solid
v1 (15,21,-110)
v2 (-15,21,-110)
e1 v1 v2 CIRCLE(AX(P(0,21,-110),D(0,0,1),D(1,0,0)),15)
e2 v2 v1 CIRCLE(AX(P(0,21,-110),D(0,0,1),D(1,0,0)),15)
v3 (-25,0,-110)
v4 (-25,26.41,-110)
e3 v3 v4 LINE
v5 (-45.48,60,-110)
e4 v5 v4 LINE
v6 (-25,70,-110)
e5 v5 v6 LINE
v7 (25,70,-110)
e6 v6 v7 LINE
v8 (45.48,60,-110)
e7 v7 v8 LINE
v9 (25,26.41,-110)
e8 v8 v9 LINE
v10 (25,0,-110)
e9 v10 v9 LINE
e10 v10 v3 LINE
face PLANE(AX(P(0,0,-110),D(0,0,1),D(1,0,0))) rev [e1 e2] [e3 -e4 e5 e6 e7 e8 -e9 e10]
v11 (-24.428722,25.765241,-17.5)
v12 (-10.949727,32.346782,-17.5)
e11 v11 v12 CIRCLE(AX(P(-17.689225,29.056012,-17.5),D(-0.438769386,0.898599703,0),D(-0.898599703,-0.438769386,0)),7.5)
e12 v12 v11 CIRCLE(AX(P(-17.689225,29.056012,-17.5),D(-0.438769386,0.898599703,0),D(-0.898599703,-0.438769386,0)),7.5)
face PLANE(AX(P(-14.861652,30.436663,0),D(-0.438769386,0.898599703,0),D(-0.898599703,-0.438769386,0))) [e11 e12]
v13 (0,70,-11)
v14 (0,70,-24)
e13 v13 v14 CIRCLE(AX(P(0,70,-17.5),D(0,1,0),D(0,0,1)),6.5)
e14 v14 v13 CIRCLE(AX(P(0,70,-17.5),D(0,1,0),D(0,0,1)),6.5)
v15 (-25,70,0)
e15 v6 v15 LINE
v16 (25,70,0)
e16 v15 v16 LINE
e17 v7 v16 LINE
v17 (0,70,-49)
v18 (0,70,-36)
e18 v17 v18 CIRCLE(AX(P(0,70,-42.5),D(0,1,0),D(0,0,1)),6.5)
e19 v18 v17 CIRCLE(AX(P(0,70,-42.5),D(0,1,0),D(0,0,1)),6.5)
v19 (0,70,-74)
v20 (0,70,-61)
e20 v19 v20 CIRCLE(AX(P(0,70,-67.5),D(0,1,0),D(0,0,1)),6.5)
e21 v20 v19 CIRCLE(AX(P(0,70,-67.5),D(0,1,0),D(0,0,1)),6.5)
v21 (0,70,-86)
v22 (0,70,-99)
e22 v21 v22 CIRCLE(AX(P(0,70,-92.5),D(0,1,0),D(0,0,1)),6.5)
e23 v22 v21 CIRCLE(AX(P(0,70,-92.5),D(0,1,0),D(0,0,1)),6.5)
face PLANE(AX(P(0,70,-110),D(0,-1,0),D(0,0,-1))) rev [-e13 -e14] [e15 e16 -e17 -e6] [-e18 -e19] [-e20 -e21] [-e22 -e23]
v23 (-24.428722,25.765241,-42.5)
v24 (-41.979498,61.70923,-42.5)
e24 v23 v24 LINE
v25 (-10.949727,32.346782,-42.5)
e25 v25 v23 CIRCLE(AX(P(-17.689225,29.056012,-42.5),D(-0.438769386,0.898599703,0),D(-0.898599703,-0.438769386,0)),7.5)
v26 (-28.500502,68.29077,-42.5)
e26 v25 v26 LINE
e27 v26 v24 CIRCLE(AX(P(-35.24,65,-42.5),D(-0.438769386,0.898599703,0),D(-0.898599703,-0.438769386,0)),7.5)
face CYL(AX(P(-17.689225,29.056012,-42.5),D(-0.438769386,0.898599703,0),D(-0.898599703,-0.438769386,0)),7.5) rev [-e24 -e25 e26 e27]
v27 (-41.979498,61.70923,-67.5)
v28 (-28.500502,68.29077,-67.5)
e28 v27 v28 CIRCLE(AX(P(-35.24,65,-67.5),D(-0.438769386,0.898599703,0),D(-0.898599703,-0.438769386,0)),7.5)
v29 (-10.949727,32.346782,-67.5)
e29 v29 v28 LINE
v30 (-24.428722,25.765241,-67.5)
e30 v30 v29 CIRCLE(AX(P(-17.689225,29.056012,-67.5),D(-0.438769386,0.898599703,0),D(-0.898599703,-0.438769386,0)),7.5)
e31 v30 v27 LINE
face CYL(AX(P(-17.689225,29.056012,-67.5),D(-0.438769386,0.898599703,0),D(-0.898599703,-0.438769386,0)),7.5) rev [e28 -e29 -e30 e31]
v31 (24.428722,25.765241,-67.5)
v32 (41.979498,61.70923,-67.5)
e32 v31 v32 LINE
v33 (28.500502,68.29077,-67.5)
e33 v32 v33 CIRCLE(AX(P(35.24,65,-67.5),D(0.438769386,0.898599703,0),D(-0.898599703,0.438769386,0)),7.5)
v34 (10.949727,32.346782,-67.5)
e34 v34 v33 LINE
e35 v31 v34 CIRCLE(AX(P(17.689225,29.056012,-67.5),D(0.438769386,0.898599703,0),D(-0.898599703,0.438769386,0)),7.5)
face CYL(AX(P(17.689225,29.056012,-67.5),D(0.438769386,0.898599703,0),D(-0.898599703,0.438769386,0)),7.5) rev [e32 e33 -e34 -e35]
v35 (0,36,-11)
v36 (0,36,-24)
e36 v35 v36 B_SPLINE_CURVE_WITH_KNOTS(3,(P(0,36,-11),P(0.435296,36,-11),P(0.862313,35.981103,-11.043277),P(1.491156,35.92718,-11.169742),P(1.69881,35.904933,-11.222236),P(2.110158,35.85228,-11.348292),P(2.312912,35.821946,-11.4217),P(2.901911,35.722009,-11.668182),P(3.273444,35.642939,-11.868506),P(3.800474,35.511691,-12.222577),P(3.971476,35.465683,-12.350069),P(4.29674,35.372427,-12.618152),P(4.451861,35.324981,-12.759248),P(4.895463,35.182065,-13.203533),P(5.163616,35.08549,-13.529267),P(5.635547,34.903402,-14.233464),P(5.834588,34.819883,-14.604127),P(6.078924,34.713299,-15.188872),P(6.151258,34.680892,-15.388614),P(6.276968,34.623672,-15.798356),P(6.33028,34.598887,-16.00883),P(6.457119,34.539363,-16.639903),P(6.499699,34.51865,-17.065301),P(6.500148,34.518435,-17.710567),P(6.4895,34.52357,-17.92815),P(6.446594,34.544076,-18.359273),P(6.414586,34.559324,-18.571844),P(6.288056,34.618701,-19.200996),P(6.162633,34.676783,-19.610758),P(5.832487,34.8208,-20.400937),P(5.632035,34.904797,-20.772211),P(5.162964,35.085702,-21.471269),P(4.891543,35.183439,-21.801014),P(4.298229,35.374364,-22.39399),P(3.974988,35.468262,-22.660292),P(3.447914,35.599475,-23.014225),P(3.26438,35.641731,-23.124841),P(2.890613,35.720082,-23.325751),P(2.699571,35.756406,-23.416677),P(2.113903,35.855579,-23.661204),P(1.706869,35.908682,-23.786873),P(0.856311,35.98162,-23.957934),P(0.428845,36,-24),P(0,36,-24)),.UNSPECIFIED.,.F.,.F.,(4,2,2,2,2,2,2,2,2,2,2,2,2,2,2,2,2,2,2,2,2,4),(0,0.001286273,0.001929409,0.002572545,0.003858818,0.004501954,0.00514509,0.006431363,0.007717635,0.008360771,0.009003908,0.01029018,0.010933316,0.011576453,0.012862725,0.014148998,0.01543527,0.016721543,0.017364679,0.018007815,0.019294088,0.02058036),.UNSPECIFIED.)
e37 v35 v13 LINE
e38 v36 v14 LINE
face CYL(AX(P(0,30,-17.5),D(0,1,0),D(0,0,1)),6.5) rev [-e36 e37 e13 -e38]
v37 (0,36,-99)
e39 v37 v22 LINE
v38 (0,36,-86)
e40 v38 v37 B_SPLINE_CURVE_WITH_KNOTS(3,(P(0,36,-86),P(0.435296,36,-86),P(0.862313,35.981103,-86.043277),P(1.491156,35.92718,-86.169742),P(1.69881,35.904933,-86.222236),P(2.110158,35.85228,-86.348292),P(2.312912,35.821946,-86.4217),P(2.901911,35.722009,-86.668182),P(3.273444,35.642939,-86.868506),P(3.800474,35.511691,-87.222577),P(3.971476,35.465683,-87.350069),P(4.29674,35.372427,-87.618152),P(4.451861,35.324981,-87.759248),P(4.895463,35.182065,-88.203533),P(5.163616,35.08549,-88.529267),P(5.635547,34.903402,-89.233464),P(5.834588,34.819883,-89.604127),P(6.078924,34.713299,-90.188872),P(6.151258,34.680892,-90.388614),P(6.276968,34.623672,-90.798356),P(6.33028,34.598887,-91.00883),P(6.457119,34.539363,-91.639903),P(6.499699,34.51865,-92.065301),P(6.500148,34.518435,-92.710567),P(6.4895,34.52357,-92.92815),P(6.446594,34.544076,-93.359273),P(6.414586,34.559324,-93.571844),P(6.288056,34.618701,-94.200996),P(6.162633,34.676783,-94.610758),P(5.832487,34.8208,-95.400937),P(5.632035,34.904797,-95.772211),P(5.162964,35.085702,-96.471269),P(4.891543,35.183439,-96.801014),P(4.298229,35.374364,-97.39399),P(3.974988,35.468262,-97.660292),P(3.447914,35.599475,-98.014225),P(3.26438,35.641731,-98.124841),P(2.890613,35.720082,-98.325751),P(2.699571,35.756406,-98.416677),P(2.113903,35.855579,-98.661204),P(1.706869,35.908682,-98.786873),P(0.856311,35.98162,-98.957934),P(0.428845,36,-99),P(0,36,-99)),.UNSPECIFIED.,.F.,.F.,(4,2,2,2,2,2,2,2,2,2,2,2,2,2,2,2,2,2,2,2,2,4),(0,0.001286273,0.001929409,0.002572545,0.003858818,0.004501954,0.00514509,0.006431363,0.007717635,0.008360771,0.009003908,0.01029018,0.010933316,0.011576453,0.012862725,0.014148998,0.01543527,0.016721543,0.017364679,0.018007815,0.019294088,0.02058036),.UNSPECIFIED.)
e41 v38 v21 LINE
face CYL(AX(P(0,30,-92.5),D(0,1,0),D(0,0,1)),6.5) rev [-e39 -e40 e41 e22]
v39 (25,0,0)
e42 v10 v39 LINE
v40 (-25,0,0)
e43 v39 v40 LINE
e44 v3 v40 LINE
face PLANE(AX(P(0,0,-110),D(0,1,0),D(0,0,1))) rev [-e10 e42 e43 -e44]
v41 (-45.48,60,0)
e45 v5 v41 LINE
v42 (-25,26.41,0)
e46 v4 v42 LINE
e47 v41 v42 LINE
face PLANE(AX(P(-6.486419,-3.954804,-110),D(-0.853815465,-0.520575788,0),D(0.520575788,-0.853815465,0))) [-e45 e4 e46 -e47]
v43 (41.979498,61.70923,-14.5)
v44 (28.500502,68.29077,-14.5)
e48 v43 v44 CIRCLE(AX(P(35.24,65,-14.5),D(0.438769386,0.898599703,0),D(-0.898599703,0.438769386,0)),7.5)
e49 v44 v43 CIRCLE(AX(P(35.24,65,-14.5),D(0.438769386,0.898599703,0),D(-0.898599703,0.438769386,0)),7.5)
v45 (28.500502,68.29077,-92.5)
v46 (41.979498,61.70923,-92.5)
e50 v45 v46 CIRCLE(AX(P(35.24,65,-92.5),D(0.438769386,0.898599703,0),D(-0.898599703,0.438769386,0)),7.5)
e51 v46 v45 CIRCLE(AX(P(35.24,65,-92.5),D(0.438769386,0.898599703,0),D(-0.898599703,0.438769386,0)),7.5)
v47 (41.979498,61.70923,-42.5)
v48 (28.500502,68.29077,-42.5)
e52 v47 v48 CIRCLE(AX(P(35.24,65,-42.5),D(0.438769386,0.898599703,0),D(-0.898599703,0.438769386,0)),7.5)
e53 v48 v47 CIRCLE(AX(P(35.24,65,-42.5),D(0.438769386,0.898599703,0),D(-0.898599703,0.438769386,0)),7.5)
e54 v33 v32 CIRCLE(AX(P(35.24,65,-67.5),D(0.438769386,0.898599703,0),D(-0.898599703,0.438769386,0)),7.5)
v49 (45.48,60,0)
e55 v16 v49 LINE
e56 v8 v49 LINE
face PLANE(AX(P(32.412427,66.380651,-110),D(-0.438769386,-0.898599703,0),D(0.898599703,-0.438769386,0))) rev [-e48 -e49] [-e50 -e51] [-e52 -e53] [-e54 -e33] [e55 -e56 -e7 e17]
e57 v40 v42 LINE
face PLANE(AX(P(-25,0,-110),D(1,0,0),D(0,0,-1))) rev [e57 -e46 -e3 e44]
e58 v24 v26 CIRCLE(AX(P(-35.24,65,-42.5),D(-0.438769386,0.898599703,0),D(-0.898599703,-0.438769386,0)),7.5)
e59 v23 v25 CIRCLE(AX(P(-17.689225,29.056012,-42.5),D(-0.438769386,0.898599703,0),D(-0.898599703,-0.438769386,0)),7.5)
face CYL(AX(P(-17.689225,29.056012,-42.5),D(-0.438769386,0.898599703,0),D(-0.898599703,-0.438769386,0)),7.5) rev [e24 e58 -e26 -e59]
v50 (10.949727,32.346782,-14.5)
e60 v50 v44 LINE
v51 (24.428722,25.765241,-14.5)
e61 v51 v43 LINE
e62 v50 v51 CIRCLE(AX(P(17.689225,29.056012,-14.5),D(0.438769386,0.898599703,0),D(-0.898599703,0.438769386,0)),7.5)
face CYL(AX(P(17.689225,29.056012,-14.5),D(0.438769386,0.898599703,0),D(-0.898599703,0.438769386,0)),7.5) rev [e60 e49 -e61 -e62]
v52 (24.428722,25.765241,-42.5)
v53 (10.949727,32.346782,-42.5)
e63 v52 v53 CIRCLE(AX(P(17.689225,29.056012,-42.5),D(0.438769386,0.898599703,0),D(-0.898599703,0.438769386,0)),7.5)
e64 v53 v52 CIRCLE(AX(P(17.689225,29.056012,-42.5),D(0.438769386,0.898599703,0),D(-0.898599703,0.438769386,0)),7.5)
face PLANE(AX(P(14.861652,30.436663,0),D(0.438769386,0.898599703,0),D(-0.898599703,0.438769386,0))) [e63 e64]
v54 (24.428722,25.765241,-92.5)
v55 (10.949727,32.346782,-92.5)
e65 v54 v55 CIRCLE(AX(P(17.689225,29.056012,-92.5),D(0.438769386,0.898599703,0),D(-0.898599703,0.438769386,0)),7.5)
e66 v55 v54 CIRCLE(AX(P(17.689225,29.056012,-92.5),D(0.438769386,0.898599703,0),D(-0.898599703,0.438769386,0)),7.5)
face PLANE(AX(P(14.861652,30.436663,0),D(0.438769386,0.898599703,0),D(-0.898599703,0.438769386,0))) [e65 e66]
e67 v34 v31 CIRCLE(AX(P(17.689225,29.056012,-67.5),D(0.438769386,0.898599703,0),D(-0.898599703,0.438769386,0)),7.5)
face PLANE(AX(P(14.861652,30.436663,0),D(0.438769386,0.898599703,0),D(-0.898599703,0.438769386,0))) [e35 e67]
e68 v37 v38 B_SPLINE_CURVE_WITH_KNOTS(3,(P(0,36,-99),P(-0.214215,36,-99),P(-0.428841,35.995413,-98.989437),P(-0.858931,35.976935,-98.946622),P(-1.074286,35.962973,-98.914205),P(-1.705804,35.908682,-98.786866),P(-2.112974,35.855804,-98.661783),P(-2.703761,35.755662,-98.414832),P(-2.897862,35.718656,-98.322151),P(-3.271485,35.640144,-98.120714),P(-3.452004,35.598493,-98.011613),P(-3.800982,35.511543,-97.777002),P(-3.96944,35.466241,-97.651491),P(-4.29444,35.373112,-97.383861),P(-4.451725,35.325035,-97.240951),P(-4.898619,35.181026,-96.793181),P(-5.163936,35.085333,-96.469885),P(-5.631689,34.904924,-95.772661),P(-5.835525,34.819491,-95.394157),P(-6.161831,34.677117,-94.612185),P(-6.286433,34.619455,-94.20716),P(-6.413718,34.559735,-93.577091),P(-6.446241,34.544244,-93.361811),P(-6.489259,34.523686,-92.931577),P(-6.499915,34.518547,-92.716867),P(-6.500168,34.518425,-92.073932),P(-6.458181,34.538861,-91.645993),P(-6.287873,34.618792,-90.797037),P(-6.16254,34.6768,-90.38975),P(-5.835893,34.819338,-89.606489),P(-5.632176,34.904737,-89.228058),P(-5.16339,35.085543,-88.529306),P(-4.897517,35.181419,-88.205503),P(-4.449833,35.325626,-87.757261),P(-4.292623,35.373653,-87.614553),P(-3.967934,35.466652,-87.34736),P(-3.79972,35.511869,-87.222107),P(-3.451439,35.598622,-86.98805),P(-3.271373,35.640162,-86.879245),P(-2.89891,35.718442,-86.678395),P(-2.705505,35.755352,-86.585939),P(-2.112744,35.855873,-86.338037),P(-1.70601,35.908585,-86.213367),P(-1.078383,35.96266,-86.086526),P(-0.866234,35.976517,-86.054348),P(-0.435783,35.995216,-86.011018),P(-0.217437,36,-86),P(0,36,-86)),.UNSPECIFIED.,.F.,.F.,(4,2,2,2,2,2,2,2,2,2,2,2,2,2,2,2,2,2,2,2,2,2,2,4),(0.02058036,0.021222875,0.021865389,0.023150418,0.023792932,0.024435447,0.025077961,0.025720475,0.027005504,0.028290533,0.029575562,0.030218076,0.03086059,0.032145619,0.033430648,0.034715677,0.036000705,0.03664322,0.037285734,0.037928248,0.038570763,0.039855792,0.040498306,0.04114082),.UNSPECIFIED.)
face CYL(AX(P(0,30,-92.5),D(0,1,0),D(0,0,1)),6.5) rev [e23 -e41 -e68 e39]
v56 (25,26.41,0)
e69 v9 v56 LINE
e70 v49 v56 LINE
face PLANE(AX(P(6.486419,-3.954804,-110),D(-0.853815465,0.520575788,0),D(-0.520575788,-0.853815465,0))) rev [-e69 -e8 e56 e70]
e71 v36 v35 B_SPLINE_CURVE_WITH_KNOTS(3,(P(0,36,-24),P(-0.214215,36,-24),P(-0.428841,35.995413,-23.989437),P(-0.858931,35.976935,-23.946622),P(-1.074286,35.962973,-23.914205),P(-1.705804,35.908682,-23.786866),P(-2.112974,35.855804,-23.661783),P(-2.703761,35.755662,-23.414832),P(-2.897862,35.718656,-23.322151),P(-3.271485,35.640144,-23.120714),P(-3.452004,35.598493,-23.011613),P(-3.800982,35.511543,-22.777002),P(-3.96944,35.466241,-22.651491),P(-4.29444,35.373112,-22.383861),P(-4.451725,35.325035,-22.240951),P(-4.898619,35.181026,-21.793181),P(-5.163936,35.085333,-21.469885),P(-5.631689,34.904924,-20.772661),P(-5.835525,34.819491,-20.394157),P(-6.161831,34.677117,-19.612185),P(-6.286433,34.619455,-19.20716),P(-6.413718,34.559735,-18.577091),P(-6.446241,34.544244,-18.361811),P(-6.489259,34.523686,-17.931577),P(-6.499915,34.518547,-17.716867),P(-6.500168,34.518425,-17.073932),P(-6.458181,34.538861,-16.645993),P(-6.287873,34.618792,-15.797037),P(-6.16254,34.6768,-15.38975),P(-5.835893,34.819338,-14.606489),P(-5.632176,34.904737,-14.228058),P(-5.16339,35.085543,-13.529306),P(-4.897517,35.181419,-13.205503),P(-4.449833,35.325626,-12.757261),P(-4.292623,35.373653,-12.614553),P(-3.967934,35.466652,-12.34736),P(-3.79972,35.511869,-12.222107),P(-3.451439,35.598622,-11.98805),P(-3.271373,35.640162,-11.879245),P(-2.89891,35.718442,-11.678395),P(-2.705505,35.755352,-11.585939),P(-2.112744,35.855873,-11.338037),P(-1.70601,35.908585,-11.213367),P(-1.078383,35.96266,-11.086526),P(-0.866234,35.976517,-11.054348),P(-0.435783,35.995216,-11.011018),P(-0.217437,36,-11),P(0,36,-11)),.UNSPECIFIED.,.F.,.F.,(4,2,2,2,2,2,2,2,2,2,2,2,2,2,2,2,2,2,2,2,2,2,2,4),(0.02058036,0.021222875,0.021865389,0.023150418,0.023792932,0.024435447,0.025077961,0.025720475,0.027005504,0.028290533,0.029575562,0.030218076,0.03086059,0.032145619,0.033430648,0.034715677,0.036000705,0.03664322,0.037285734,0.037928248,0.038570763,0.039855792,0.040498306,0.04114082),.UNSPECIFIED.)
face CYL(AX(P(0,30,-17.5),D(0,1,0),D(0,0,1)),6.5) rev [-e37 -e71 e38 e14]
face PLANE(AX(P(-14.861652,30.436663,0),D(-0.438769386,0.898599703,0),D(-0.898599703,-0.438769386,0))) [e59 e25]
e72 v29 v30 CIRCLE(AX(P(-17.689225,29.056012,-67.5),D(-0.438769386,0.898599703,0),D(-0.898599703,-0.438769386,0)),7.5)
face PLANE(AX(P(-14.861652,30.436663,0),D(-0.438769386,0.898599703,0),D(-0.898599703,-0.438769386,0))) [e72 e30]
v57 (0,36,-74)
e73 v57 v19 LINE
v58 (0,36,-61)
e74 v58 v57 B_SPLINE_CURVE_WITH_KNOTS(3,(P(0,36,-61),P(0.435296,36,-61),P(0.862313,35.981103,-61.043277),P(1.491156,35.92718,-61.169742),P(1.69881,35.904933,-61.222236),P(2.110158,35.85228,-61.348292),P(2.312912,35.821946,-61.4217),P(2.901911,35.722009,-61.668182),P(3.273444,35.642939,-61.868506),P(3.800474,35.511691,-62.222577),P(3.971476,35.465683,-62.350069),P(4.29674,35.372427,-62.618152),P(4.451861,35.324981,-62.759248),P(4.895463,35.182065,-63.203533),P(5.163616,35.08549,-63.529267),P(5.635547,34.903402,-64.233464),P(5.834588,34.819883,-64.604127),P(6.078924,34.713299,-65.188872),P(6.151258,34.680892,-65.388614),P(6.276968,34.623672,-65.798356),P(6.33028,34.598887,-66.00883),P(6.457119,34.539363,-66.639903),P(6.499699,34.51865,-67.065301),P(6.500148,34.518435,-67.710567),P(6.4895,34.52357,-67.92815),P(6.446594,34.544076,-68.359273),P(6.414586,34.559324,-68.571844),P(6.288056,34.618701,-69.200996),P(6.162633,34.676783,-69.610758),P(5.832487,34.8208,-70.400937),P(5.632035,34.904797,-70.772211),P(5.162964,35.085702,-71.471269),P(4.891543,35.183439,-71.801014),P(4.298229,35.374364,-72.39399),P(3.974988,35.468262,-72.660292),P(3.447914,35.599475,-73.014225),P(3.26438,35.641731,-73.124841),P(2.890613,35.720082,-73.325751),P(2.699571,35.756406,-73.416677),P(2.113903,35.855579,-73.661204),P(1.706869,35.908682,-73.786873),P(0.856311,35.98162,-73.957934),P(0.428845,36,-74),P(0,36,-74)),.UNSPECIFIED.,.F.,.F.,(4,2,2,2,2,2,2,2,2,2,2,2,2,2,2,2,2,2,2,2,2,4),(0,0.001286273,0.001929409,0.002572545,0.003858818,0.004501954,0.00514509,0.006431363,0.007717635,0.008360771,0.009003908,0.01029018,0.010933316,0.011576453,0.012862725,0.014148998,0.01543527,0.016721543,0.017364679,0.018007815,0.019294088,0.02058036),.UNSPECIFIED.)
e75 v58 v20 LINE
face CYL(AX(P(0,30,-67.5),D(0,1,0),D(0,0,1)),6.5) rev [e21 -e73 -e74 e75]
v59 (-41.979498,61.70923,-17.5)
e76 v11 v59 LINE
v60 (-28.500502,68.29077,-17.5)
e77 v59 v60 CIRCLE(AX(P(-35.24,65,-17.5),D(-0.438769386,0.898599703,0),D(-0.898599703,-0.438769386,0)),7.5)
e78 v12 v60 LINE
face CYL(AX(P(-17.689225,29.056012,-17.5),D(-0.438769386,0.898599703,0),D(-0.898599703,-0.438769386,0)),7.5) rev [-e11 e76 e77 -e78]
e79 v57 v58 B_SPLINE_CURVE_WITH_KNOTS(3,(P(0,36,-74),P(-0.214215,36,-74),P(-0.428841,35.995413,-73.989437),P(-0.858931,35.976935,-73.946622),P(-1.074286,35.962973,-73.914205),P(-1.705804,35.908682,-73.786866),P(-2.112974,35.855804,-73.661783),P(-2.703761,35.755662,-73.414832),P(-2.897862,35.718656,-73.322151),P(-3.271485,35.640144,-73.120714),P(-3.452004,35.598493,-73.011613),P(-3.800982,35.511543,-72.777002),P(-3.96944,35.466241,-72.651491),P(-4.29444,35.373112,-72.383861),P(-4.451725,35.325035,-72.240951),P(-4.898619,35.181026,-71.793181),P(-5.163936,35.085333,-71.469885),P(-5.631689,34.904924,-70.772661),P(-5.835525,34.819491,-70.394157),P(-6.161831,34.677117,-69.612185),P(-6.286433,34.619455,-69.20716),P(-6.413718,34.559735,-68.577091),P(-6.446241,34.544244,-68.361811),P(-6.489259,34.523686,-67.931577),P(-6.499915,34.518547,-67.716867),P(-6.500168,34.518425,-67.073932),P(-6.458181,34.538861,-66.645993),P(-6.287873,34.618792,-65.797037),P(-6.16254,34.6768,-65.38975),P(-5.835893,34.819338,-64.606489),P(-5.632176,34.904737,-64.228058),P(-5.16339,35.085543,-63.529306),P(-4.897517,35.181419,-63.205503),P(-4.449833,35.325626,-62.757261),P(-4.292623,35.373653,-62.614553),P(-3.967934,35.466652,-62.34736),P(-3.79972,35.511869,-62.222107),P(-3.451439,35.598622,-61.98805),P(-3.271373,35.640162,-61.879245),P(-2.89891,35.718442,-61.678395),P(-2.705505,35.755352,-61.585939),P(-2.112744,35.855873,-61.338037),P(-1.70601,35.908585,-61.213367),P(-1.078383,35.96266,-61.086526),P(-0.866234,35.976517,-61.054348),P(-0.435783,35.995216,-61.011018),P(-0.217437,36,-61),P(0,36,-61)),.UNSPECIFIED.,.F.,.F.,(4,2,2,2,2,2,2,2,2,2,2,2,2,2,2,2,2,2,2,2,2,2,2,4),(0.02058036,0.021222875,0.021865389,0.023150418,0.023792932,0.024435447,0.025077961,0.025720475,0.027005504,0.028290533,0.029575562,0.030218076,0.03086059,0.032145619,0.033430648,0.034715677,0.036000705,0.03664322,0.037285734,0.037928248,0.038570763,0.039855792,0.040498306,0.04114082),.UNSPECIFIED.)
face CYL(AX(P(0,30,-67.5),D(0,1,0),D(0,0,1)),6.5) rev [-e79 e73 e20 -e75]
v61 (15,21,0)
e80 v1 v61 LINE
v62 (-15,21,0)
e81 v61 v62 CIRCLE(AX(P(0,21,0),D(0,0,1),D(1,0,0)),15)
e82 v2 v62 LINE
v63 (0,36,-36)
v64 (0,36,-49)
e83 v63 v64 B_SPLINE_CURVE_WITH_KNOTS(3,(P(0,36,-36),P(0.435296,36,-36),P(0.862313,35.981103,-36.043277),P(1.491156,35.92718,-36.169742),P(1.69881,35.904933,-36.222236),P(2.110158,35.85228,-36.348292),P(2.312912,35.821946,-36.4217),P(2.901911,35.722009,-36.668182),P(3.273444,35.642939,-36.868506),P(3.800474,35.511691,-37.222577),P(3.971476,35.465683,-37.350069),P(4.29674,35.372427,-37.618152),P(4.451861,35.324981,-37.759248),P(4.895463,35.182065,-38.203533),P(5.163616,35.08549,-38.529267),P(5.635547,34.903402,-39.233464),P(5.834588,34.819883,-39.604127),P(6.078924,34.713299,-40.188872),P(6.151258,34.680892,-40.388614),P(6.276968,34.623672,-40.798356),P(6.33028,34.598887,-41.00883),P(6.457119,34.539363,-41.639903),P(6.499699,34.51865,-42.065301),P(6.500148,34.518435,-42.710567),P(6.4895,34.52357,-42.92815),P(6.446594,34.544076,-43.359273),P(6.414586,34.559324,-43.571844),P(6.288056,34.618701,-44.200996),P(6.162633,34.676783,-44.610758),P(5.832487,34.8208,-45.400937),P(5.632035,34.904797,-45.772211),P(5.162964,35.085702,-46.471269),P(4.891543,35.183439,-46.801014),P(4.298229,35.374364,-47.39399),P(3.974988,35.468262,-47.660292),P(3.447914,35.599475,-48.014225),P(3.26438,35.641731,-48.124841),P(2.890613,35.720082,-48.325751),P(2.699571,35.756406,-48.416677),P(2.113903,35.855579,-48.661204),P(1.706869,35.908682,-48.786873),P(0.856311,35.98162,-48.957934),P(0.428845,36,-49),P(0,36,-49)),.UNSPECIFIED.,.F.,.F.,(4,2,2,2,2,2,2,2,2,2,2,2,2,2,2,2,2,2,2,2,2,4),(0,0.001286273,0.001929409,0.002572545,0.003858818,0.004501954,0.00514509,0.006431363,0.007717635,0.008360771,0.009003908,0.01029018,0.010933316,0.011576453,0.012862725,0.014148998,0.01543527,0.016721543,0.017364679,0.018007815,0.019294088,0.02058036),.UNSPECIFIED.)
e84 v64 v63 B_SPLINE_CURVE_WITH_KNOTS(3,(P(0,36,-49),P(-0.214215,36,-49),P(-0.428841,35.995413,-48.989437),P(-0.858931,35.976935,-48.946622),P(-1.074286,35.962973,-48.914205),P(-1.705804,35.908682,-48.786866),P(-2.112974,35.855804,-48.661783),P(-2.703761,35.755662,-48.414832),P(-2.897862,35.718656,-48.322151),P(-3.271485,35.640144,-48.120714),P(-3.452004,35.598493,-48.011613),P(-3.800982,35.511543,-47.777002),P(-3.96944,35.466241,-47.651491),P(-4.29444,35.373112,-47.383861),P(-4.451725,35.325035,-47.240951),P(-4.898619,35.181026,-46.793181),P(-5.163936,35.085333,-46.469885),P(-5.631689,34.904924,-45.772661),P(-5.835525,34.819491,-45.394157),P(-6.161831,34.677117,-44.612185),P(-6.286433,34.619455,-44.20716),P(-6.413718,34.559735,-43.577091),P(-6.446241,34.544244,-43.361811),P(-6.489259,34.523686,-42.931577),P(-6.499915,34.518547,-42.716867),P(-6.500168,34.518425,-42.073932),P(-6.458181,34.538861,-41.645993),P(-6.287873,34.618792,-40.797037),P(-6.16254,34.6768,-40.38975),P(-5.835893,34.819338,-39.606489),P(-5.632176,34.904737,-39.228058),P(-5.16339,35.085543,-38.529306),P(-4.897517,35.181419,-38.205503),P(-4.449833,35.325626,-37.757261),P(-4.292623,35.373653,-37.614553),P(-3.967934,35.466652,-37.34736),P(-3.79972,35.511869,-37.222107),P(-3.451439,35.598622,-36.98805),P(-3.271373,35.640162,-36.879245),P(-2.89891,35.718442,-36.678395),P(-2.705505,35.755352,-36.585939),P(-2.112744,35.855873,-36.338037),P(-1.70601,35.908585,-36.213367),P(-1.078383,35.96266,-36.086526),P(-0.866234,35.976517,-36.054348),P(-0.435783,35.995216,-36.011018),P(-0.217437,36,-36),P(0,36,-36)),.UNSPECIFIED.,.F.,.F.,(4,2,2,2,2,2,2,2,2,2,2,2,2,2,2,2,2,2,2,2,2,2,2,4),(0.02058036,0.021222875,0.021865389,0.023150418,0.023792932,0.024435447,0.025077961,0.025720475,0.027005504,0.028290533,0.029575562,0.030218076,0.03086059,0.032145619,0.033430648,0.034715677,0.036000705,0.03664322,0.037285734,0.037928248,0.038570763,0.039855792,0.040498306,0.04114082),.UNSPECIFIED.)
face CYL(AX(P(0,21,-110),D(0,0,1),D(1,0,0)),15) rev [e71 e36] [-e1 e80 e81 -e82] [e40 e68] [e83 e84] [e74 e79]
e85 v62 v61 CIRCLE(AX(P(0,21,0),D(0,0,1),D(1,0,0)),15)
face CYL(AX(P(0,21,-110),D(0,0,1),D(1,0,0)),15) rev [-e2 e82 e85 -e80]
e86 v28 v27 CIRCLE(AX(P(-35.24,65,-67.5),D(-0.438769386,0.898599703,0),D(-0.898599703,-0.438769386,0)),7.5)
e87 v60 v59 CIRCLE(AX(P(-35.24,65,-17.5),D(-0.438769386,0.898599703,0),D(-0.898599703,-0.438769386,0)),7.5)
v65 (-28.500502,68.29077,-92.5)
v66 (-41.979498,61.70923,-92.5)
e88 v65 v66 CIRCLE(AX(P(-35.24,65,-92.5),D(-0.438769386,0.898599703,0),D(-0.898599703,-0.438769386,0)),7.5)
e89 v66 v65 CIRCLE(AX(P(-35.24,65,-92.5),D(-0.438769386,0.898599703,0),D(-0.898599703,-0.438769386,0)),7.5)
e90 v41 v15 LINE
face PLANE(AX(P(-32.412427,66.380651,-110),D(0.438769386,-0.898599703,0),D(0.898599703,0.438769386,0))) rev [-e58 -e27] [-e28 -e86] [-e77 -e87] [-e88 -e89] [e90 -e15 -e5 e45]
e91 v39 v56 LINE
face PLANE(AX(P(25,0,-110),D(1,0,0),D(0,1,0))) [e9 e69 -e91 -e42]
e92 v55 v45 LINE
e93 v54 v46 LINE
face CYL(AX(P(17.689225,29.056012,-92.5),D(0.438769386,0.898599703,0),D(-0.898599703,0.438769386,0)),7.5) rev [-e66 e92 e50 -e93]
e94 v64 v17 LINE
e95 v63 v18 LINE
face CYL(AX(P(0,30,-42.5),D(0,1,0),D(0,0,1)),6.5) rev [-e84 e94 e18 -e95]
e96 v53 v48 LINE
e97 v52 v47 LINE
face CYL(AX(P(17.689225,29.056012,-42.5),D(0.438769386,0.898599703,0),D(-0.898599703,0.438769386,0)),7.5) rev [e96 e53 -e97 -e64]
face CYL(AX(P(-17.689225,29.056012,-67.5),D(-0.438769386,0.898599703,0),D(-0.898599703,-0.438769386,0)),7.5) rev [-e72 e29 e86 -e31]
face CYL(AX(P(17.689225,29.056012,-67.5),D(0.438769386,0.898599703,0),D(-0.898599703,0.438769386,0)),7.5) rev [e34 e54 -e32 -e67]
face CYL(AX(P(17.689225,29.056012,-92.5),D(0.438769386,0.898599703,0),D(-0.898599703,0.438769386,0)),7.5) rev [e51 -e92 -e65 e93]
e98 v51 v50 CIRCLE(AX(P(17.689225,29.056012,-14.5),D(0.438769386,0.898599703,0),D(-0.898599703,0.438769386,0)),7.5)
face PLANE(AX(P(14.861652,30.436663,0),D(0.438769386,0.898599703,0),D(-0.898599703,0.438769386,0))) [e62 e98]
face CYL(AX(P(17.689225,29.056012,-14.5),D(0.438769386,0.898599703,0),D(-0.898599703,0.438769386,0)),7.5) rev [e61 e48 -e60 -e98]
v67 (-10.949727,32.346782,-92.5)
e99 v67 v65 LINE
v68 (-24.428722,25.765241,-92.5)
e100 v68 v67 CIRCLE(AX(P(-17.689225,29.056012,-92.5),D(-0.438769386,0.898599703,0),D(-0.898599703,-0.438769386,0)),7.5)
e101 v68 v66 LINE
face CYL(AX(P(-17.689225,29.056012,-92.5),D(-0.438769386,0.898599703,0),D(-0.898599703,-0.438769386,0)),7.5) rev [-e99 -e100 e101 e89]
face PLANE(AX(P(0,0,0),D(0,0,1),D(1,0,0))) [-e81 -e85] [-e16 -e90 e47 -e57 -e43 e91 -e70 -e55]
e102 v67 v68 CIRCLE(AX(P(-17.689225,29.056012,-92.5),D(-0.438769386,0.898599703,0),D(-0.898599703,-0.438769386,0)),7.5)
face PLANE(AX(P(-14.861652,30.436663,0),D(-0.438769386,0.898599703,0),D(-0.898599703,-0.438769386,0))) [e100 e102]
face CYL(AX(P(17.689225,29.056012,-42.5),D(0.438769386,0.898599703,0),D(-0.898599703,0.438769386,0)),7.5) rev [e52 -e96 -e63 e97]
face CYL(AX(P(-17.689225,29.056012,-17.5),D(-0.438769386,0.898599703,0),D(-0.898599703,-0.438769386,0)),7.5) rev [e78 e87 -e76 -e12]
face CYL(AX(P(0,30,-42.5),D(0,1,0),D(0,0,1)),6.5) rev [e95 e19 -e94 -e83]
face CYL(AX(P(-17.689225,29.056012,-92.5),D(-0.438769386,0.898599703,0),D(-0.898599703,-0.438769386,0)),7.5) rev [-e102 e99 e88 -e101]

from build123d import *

# Parameters (mm, degrees)
BLOCK_PROFILE_SKETCH_R      = 15
ENGINE_BLOCK_DEPTH          = 110
BANK_1_CYLINDER_BORES_DEPTH = 40
BANK_2_BORES_SKETCH_R       = 7.5
BANK_2_CYLINDER_BORES_DEPTH = 40
TOP_DECK_BORES_SKETCH_R     = 6.5
TOP_DECK_BORES_DEPTH        = 40


with BuildPart() as part:
    # Block Profile Sketch → Engine Block (new body)
    with BuildSketch(Plane.XY):
        Polygon((-25, 0), (0, 0), (25, 0), (25, 26.41), (45.48, 60), (25, 70), (0, 70), (-25, 70), (-45.48, 60), (-25, 26.41), align=None)
        with Locations((0, 21)):
            Circle(BLOCK_PROFILE_SKETCH_R, mode=Mode.SUBTRACT)
    extrude(amount=-ENGINE_BLOCK_DEPTH)

    # Bank 1 Bores Sketch → Bank 1 Cylinder Bores (cut)
    with BuildSketch(Plane(origin=(32.412427151, 66.380650805, 0), x_dir=(0.8985997027642283, -0.43876938611534955, 0), z_dir=(0.4387693861153495, 0.8985997027642282, 0))):
        with BuildLine():
            ThreePointArc((3.146643428, 100), (-4.353356572, 92.5), (3.146643428, 85))
            Line((3.146643428, 85), (3.146643428, 92.5))
            Line((3.146643428, 92.5), (3.146643428, 100))
        make_face()
        with BuildLine():
            Line((3.146643428, 92.5), (3.146643428, 85))
            ThreePointArc((3.146643428, 85), (8.449944287, 87.196699141), (10.646643428, 92.5))
            Line((10.646643428, 92.5), (3.146643428, 92.5))
        make_face()
        with BuildLine():
            Line((3.146643428, 100), (3.146643428, 92.5))
            Line((3.146643428, 92.5), (10.646643428, 92.5))
            ThreePointArc((10.646643428, 92.5), (8.449944287, 97.803300859), (3.146643428, 100))
        make_face()
        with BuildLine():
            Line((3.146643428, 92.5), (3.146643428, 85))
            ThreePointArc((3.146643428, 85), (8.449944287, 87.196699141), (10.646643428, 92.5))
            Line((10.646643428, 92.5), (3.146643428, 92.5))
        make_face()
        with BuildLine():
            Line((3.146643428, 100), (3.146643428, 92.5))
            Line((3.146643428, 92.5), (10.646643428, 92.5))
            ThreePointArc((10.646643428, 92.5), (8.449944287, 97.803300859), (3.146643428, 100))
        make_face()
        with BuildLine():
            Line((3.146643428, 67.5), (3.146643428, 60))
            ThreePointArc((3.146643428, 60), (8.449944287, 62.196699141), (10.646643428, 67.5))
            Line((10.646643428, 67.5), (3.146643428, 67.5))
        make_face()
        with BuildLine():
            Line((3.146643428, 75), (3.146643428, 67.5))
            Line((3.146643428, 67.5), (10.646643428, 67.5))
            ThreePointArc((10.646643428, 67.5), (8.449944287, 72.803300859), (3.146643428, 75))
        make_face()
        with BuildLine():
            Line((3.146643428, 67.5), (3.146643428, 60))
            ThreePointArc((3.146643428, 60), (8.449944287, 62.196699141), (10.646643428, 67.5))
            Line((10.646643428, 67.5), (3.146643428, 67.5))
        make_face()
        with BuildLine():
            Line((3.146643428, 75), (3.146643428, 67.5))
            Line((3.146643428, 67.5), (10.646643428, 67.5))
            ThreePointArc((10.646643428, 67.5), (8.449944287, 72.803300859), (3.146643428, 75))
        make_face()
        with BuildLine():
            ThreePointArc((3.146643428, 75), (-4.353356572, 67.5), (3.146643428, 60))
            Line((3.146643428, 60), (3.146643428, 67.5))
            Line((3.146643428, 67.5), (3.146643428, 75))
        make_face()
        with BuildLine():
            ThreePointArc((3.146643428, 50), (-4.353356572, 42.5), (3.146643428, 35))
            Line((3.146643428, 35), (3.146643428, 42.5))
            Line((3.146643428, 42.5), (3.146643428, 50))
        make_face()
        with BuildLine():
            Line((3.146643428, 42.5), (3.146643428, 35))
            ThreePointArc((3.146643428, 35), (8.449944287, 37.196699141), (10.646643428, 42.5))
            Line((10.646643428, 42.5), (3.146643428, 42.5))
        make_face()
        with BuildLine():
            Line((3.146643428, 50), (3.146643428, 42.5))
            Line((3.146643428, 42.5), (10.646643428, 42.5))
            ThreePointArc((10.646643428, 42.5), (8.449944287, 47.803300859), (3.146643428, 50))
        make_face()
        with BuildLine():
            Line((3.146643428, 42.5), (3.146643428, 35))
            ThreePointArc((3.146643428, 35), (8.449944287, 37.196699141), (10.646643428, 42.5))
            Line((10.646643428, 42.5), (3.146643428, 42.5))
        make_face()
        with BuildLine():
            Line((3.146643428, 50), (3.146643428, 42.5))
            Line((3.146643428, 42.5), (10.646643428, 42.5))
            ThreePointArc((10.646643428, 42.5), (8.449944287, 47.803300859), (3.146643428, 50))
        make_face()
        with BuildLine():
            ThreePointArc((3.146643428, 22), (-4.353356572, 14.5), (3.146643428, 7))
            Line((3.146643428, 7), (3.146643428, 14.5))
            Line((3.146643428, 14.5), (3.146643428, 22))
        make_face()
        with BuildLine():
            Line((3.146643428, 14.5), (3.146643428, 7))
            ThreePointArc((3.146643428, 7), (8.449944287, 9.196699141), (10.646643428, 14.5))
            Line((10.646643428, 14.5), (3.146643428, 14.5))
        make_face()
        with BuildLine():
            Line((3.146643428, 22), (3.146643428, 14.5))
            Line((3.146643428, 14.5), (10.646643428, 14.5))
            ThreePointArc((10.646643428, 14.5), (8.449944287, 19.803300859), (3.146643428, 22))
        make_face()
        with BuildLine():
            Line((3.146643428, 14.5), (3.146643428, 7))
            ThreePointArc((3.146643428, 7), (8.449944287, 9.196699141), (10.646643428, 14.5))
            Line((10.646643428, 14.5), (3.146643428, 14.5))
        make_face()
        with BuildLine():
            Line((3.146643428, 22), (3.146643428, 14.5))
            Line((3.146643428, 14.5), (10.646643428, 14.5))
            ThreePointArc((10.646643428, 14.5), (8.449944287, 19.803300859), (3.146643428, 22))
        make_face()
    extrude(amount=-BANK_1_CYLINDER_BORES_DEPTH, mode=Mode.SUBTRACT)

    # Bank 2 Bores Sketch → Bank 2 Cylinder Bores (cut)
    with BuildSketch(Plane(origin=(-32.412427151, 66.380650805, 0), x_dir=(0.8985997027642294, 0.43876938611534716, 0), z_dir=(-0.4387693861153471, 0.8985997027642293, 0))):
        with Locations(Location((-3.146643428, 92.5, 0), (0, 0, 180))):
            Circle(BANK_2_BORES_SKETCH_R)
        with Locations(Location((-3.146643428, 67.5, 0), (0, 0, 180))):
            Circle(BANK_2_BORES_SKETCH_R)
        with Locations(Location((-3.146643428, 42.5, 0), (0, 0, 180))):
            Circle(BANK_2_BORES_SKETCH_R)
        with Locations(Location((-3.146643428, 17.5, 0), (0, 0, 180))):
            Circle(BANK_2_BORES_SKETCH_R)
    extrude(amount=-BANK_2_CYLINDER_BORES_DEPTH, mode=Mode.SUBTRACT)

    # Top Deck Bores Sketch → Top Deck Bores (cut)
    with BuildSketch(Plane(origin=(0, 70, 0), x_dir=(1, 0, 0), z_dir=(0, 1, 0))):
        with Locations(Location((0, 92.5, 0), (0, 0, 270))):
            Circle(TOP_DECK_BORES_SKETCH_R)
        with Locations(Location((0, 67.5, 0), (0, 0, 270))):
            Circle(TOP_DECK_BORES_SKETCH_R)
        with Locations(Location((0, 42.5, 0), (0, 0, 270))):
            Circle(TOP_DECK_BORES_SKETCH_R)
        with Locations(Location((0, 17.5, 0), (0, 0, 270))):
            Circle(TOP_DECK_BORES_SKETCH_R)
    extrude(amount=-TOP_DECK_BORES_DEPTH, mode=Mode.SUBTRACT)


solid = part.part
